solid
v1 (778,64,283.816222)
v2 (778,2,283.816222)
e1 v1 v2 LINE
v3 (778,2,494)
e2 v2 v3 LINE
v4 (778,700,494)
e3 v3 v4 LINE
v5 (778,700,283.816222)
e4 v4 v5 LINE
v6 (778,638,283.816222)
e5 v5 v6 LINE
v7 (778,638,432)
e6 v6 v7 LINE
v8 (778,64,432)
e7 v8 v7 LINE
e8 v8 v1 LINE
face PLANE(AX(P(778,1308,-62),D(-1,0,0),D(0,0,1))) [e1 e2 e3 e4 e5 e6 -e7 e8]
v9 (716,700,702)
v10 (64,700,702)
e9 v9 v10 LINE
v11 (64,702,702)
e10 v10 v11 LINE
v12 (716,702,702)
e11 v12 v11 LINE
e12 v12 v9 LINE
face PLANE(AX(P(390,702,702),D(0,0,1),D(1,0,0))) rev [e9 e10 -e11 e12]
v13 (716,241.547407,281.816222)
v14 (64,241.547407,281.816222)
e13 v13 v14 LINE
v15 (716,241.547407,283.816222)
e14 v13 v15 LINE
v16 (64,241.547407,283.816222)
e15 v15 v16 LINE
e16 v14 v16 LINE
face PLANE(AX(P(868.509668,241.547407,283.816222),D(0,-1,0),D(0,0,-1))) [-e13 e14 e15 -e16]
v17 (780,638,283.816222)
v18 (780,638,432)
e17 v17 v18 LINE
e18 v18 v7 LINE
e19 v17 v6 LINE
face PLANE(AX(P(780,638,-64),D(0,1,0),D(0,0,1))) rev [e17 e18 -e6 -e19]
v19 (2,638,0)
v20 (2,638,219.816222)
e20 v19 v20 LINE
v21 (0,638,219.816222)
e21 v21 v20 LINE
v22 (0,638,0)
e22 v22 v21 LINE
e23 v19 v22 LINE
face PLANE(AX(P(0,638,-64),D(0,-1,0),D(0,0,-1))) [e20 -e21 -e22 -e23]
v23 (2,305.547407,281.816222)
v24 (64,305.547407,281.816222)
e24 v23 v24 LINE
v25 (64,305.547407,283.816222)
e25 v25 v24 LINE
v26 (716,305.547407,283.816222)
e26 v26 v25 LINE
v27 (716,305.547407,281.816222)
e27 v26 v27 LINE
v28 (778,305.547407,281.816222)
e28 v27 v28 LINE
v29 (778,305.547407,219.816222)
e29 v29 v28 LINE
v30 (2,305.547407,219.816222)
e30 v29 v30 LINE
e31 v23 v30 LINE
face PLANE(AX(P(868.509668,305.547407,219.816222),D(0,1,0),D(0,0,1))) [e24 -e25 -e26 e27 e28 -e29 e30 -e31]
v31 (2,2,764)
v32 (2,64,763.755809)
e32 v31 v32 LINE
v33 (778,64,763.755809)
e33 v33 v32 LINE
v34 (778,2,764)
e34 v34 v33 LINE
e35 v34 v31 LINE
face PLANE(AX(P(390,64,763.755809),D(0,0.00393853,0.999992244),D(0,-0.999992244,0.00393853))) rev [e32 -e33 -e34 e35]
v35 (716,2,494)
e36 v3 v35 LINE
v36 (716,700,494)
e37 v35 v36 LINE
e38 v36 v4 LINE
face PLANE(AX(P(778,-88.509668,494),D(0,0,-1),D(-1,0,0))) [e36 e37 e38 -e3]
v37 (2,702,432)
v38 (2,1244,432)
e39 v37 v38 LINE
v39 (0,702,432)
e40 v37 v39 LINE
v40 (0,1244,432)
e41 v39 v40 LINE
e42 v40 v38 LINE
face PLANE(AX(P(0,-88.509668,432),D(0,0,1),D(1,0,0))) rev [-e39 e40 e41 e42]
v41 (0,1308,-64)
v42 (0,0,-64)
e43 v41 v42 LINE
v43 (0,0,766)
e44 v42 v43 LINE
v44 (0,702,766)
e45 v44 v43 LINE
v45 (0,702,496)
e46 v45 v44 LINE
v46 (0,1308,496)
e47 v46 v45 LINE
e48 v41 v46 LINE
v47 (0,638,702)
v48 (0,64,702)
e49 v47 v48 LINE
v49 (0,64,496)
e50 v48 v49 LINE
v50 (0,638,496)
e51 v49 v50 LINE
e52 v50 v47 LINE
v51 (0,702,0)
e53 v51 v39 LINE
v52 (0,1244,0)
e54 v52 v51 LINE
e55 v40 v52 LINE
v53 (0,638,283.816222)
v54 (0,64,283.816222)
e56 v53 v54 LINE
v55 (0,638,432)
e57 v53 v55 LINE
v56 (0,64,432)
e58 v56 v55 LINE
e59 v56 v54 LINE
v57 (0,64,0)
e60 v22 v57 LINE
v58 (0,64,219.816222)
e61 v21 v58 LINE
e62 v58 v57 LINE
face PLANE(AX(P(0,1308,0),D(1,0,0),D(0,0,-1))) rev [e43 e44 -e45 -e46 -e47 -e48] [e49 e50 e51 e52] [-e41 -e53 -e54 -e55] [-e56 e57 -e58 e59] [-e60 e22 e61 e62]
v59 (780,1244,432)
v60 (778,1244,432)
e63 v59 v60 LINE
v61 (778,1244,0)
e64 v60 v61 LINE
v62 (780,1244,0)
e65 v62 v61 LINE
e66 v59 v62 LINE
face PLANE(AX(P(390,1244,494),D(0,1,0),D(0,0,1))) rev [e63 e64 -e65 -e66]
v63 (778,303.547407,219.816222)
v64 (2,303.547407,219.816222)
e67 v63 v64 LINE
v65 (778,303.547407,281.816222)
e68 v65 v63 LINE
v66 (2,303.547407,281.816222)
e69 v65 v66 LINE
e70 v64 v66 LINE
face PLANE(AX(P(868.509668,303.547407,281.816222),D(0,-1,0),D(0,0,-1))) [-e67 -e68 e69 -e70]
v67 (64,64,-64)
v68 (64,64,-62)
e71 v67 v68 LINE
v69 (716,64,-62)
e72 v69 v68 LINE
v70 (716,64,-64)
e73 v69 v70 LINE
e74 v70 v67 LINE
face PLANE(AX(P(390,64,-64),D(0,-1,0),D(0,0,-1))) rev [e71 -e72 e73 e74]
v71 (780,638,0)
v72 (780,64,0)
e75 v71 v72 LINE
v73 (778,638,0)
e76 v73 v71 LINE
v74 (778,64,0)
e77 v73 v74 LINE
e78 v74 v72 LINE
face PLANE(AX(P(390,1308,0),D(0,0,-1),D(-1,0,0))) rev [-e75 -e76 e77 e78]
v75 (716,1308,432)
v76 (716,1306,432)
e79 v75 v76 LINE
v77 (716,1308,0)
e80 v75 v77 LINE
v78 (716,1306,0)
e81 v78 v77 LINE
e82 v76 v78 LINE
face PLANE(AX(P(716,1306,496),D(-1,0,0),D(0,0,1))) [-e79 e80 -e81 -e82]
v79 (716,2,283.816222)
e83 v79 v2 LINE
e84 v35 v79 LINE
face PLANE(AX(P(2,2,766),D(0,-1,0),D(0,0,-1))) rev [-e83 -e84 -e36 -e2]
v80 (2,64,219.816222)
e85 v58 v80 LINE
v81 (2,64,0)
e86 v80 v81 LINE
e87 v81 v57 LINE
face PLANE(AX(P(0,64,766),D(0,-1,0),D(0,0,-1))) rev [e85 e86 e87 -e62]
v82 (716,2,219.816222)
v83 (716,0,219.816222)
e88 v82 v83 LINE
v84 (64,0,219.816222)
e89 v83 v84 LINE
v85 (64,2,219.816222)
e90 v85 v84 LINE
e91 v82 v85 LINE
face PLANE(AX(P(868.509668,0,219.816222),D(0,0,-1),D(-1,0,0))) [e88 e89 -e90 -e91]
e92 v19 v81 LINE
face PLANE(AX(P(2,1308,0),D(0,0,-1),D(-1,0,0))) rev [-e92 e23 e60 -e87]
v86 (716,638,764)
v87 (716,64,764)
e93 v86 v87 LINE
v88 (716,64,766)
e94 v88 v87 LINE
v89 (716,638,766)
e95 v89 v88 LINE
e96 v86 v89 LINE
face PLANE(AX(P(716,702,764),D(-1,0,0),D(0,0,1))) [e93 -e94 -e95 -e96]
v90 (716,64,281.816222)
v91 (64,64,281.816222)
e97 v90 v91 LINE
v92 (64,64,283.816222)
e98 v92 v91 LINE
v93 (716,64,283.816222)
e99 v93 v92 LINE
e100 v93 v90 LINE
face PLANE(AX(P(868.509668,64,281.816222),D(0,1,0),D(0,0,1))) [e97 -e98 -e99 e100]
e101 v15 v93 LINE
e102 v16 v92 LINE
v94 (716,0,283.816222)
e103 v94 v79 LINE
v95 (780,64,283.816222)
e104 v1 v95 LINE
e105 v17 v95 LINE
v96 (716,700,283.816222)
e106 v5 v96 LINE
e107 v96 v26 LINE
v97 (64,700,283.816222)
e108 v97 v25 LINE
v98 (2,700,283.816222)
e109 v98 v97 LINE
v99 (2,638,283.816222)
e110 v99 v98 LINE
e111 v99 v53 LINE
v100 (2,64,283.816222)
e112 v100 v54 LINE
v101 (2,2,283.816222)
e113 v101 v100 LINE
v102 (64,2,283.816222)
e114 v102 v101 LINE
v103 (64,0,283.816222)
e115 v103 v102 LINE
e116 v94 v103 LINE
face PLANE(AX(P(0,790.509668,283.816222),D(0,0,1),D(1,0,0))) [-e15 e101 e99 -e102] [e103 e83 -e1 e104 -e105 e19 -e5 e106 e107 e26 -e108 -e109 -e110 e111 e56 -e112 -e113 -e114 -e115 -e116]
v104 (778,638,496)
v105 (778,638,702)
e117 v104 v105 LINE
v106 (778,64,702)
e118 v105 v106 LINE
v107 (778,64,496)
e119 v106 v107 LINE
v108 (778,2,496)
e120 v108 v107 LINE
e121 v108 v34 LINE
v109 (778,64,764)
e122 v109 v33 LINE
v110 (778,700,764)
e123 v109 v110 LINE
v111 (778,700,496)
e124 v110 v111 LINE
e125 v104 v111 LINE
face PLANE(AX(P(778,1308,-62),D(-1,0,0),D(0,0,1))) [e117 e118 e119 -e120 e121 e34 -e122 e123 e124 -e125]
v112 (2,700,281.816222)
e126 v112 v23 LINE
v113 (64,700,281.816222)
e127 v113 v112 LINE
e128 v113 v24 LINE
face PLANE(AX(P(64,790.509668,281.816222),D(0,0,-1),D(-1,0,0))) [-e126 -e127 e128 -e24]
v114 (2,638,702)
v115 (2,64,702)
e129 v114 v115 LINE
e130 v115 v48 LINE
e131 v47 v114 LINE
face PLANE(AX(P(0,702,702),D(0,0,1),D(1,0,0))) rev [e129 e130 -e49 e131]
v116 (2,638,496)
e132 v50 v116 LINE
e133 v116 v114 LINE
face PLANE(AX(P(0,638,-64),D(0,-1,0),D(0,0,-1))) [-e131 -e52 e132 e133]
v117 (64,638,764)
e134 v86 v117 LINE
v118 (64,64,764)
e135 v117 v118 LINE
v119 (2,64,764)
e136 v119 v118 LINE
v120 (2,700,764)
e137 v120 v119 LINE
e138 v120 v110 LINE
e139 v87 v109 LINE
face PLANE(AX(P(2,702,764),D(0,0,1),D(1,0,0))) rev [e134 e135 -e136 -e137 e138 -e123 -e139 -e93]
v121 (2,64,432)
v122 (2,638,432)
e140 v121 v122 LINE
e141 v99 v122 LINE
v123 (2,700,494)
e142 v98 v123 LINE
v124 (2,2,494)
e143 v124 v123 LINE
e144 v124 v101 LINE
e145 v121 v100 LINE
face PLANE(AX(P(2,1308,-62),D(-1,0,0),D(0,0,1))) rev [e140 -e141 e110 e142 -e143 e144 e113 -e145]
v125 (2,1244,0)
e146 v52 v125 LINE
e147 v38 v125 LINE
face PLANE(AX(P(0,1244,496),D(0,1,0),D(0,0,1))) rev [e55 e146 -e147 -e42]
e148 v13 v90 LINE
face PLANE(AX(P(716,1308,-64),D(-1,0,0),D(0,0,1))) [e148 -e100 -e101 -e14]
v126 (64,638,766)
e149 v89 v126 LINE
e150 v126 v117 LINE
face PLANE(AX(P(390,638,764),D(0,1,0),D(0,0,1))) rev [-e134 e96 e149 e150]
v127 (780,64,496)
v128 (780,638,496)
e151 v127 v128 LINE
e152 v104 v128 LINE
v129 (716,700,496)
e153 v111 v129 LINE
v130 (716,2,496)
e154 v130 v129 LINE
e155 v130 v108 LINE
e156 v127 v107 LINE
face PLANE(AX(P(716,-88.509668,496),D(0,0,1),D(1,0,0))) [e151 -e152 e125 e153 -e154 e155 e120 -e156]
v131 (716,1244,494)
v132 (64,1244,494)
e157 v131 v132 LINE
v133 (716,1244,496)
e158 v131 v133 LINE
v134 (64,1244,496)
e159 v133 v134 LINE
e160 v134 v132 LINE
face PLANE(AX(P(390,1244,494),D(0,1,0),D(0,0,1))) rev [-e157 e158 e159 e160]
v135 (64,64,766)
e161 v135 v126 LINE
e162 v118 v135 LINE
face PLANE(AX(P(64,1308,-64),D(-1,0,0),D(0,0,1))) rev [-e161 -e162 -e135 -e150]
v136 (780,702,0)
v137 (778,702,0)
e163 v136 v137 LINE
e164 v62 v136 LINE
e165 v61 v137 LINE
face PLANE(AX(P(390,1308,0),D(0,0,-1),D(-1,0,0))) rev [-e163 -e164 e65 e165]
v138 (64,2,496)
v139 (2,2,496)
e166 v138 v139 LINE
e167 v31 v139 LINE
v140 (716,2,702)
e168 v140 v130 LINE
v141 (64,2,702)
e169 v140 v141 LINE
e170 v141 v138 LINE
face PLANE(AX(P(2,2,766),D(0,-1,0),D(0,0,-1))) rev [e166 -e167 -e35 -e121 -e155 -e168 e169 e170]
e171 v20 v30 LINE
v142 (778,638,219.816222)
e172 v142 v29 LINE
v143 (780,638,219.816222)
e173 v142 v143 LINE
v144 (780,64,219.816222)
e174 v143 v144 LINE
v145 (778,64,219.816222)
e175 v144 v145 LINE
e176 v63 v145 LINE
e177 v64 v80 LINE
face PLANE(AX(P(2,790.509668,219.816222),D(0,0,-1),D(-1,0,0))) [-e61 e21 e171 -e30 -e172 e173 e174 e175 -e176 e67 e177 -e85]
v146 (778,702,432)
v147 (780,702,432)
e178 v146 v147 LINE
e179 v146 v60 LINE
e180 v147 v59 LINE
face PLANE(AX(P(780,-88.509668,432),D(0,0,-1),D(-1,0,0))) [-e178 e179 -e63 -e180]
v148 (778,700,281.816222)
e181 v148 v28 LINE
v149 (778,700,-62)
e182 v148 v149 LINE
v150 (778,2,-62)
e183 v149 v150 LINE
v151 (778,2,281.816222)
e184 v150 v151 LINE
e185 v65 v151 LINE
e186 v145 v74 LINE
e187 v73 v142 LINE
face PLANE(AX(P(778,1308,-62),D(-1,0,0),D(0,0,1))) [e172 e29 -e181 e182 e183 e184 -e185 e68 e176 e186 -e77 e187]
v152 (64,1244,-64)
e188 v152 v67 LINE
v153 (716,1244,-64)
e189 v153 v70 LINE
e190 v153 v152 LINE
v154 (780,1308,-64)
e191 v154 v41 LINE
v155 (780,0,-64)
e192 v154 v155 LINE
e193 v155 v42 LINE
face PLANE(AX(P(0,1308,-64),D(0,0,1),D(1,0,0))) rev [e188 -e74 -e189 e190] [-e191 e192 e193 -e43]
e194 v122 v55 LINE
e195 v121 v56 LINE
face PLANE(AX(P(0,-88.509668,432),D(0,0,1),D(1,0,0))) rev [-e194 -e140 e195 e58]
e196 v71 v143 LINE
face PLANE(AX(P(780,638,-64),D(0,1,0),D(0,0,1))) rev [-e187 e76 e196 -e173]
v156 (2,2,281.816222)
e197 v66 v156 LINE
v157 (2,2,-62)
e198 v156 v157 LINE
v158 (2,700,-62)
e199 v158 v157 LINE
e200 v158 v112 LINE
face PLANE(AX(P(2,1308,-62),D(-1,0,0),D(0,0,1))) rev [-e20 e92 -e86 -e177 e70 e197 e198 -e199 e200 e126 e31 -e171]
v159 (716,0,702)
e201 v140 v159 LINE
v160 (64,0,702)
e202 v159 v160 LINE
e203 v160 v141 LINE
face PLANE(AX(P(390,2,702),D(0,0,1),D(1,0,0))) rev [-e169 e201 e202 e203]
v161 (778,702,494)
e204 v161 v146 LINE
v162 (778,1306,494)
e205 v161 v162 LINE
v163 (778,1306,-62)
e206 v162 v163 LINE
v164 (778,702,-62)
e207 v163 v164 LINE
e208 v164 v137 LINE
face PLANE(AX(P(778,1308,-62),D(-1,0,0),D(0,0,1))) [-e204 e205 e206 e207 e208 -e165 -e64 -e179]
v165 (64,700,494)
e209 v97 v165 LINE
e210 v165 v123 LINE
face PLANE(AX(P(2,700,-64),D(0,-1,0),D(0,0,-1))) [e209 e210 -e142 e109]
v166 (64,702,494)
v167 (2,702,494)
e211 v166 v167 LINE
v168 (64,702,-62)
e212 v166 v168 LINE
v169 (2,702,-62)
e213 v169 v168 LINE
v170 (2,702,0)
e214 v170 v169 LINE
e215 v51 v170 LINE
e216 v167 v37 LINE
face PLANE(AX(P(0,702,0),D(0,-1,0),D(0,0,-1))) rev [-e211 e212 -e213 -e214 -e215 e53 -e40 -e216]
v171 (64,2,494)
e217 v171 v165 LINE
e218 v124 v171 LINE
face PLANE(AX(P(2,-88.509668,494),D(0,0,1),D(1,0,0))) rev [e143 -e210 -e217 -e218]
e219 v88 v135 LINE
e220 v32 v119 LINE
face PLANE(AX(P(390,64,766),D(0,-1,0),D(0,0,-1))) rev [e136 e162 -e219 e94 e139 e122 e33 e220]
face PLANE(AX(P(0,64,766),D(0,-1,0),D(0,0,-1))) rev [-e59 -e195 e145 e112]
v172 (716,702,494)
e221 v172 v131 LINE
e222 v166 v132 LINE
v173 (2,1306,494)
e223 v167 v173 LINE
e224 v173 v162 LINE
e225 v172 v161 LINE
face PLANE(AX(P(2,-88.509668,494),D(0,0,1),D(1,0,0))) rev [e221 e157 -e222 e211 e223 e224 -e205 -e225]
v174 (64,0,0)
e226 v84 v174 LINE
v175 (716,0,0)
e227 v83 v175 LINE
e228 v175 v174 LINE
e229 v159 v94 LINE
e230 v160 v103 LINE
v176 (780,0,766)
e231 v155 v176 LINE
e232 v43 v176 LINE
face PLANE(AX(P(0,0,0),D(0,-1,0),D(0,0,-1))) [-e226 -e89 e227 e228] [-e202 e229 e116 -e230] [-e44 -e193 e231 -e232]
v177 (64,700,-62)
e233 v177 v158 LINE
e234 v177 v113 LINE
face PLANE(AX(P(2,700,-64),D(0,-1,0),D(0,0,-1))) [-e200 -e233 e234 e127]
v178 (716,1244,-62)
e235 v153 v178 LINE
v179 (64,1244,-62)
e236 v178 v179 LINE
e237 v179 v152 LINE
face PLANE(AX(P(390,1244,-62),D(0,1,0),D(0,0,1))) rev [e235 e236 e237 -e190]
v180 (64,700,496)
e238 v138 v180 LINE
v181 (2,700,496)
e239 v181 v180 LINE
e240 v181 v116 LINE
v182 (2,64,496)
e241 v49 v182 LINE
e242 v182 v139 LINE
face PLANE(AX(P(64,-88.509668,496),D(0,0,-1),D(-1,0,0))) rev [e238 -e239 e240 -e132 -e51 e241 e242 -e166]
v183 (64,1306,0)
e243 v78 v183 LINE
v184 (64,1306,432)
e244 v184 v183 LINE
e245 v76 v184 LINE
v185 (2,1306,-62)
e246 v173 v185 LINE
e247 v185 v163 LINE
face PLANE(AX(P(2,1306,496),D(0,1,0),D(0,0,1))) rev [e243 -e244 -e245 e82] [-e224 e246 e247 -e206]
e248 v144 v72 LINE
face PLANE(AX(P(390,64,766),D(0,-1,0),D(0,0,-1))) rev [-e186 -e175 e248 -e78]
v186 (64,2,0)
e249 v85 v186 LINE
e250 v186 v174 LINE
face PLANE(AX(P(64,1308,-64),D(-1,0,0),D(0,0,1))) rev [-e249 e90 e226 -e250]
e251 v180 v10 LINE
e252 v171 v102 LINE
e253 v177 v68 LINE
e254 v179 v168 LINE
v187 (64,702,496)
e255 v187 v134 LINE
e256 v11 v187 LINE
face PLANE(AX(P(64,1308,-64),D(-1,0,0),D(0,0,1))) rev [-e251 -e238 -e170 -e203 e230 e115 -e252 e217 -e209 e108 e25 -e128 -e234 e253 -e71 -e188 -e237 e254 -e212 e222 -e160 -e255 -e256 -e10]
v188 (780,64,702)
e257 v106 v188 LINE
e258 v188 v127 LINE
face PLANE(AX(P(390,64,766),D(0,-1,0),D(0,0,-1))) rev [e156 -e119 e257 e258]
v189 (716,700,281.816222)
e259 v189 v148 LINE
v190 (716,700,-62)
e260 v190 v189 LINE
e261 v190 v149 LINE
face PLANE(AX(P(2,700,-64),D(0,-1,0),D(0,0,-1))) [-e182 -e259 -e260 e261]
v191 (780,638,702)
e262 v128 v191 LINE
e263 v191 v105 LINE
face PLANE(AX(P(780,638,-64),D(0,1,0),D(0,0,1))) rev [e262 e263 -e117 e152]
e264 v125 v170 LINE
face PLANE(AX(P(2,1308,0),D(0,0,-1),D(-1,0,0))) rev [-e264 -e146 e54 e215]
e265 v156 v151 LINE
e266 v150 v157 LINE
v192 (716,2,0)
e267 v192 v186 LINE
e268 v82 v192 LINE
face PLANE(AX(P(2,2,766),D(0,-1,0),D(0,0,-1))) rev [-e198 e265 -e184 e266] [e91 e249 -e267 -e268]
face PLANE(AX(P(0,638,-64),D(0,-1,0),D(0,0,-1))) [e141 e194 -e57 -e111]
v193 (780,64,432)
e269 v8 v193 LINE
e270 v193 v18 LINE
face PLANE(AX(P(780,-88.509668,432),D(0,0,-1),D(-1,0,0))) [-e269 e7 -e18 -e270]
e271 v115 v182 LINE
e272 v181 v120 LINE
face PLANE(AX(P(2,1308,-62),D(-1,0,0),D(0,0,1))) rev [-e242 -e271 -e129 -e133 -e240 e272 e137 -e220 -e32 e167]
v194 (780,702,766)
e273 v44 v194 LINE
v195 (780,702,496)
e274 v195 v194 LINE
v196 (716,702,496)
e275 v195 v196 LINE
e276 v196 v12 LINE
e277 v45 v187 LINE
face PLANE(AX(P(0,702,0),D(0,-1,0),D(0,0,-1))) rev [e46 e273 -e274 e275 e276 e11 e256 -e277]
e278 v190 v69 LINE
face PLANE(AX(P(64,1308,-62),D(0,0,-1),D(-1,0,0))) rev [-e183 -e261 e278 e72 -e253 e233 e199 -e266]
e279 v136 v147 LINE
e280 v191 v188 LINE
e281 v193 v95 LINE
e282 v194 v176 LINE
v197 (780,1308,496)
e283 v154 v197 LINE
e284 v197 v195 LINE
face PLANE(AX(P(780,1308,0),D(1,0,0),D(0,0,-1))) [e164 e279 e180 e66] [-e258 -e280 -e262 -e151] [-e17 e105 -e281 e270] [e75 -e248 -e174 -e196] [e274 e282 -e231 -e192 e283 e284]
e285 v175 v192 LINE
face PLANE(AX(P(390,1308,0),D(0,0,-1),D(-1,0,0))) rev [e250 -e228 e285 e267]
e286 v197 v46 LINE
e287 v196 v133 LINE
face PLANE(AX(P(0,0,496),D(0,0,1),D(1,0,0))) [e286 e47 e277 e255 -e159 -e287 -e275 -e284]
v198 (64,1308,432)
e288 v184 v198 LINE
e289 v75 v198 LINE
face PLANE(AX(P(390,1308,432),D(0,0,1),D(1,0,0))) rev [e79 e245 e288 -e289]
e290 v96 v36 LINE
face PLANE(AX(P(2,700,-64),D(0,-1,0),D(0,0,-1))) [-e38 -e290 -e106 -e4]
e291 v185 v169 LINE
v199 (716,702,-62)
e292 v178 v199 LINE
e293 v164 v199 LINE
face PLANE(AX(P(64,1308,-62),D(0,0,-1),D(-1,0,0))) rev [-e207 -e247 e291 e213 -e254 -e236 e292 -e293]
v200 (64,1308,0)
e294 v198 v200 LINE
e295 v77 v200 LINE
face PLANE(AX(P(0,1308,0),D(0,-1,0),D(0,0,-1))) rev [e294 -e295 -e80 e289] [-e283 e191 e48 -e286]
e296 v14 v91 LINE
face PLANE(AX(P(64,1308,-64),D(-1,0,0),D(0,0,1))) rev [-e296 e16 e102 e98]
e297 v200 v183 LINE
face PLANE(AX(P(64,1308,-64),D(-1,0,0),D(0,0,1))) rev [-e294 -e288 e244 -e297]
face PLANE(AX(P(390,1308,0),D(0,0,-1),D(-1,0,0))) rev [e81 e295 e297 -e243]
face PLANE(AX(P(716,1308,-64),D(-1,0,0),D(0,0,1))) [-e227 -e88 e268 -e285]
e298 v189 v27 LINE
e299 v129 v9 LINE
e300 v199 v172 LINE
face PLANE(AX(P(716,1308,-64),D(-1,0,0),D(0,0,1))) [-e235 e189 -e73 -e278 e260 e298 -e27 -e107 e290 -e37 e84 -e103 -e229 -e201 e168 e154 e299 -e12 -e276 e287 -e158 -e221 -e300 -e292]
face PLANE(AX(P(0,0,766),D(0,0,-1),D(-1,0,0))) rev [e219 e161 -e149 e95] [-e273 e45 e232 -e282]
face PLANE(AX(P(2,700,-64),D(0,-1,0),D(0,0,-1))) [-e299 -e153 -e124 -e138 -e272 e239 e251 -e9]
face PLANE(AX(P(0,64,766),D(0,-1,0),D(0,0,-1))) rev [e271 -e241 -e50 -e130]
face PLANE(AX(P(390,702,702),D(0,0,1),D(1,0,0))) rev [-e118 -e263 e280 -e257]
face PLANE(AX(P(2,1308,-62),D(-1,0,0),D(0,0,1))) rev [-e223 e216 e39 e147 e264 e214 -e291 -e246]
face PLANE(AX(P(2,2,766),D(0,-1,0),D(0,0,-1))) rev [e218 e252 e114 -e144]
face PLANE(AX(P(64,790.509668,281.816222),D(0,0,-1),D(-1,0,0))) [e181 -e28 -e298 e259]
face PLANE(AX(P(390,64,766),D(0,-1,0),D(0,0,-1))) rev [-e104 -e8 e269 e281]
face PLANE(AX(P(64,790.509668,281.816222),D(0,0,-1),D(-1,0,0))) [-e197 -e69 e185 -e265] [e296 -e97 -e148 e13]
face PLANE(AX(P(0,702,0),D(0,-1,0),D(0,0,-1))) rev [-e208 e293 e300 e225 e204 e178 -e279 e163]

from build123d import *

# Parameters (mm, degrees)
BOSS_EXTRUDE1_DEPTH   = 1308
BOSS_EXTRUDE2_DEPTH   = 828
BOSS_EXTRUDE3_DEPTH   = 700
BOSS_EXTRUDE4_DEPTH   = 828
BOSS_EXTRUDE5_DEPTH   = 558
BOSS_EXTRUDE6_REACH   = 1517.417
BOSS_EXTRUDE8_DEPTH   = 388
MIRROR4_COPY_1_DEPTH  = 1308
MIRROR4_COPY_2_DEPTH  = 828
MIRROR4_COPY_3_DEPTH  = 700
MIRROR4_COPY_4_DEPTH  = 828
MIRROR4_COPY_5_DEPTH  = 558
MIRROR4_COPY_6_REACH  = 1517.417
MIRROR4_COPY_7_DEPTH  = 388
MIRROR4_COPY_8_DEPTH  = 1308
MIRROR4_COPY_9_DEPTH  = 828
MIRROR4_COPY_10_DEPTH = 700
MIRROR4_COPY_11_DEPTH = 828
MIRROR4_COPY_12_DEPTH = 558
MIRROR4_COPY_13_REACH = 1517.417
MIRROR4_COPY_14_DEPTH = 388
BOSS_EXTRUDE9_REACH   = 1706.705
BOSS_EXTRUDE10_DEPTH  = 778
BOSS_EXTRUDE11_START  = -778
BOSS_EXTRUDE11_DEPTH  = 776


with BuildPart() as part:
    # Sketch1 → Boss-Extrude1 (new body)
    with BuildSketch(Plane(origin=(0, 0, 0), x_dir=(1, 0, 0), z_dir=(0, 1, 0))):
        Polygon((0, 0), (0, 64), (64, 64), (64, 62), (2, 62), (2, 0), align=None)
    boss_extrude1 = extrude(amount=BOSS_EXTRUDE1_DEPTH)

    # Sketch2 → Boss-Extrude2 (add)
    with BuildSketch(Plane.XY.offset(-62)):
        Polygon((64, 0), (0, 0), (0, 64), (2, 64), (2, 2), (64, 2), align=None)
    boss_extrude2 = extrude(amount=BOSS_EXTRUDE2_DEPTH)

    # Sketch3 → Boss-Extrude3 (add)
    with BuildSketch(Plane(origin=(0, 2, 0), x_dir=(1, 0, 0), z_dir=(0, 1, 0))):
        Polygon((64, -766), (0, -766), (0, -702), (2, -702), (2, -764), (64, -764), align=None)
    boss_extrude3 = extrude(amount=BOSS_EXTRUDE3_DEPTH)

    # Sketch4 → Boss-Extrude4 (add)
    with BuildSketch(Plane(origin=(0, 0, 764), x_dir=(-1, 0, 0), z_dir=(0, 0, -1))):
        Polygon((-64, 702), (0, 702), (0, 638), (-2, 638), (-2, 700), (-64, 700), align=None)
    boss_extrude4 = extrude(amount=BOSS_EXTRUDE4_DEPTH)

    # Sketch5 → Boss-Extrude5 (add)
    with BuildSketch(Plane.XY.offset(-62)):
        Polygon((64, 1308), (0, 1308), (0, 1244), (2, 1244), (2, 1306), (64, 1306), align=None)
    boss_extrude5 = extrude(amount=BOSS_EXTRUDE5_DEPTH)

    # Boss-Extrude6: up to this face of the body (flat: up to its plane)
    boss_extrude6_end = Plane(part.part.faces().sort_by_distance((33, 2, 351))[0])
    # Sketch6 → Boss-Extrude6 (add, up to the picked face)
    with BuildSketch(Plane.XZ.offset(-1306), mode=Mode.PRIVATE) as boss_extrude6_sk1:
        Polygon((64, 496), (0, 496), (0, 432), (2, 432), (2, 494), (64, 494), align=None)
    boss_extrude6_tool1 = split(extrude(boss_extrude6_sk1.sketch, amount=BOSS_EXTRUDE6_REACH, mode=Mode.PRIVATE), bisect_by=boss_extrude6_end, keep=Keep.BOTH, mode=Mode.PRIVATE)
    boss_extrude6 = boss_extrude6_tool1.solids().sort_by(Axis((32, 1306, 495.094903), (0, -1, 0)))[0]
    add(boss_extrude6)

    # Sketch7 → Boss-Extrude8 (add)
    with BuildSketch(Plane(origin=(2, 0, 0), x_dir=(0, 0, -1), z_dir=(1, 0, 0))):
        Polygon((-496, 1308), (-432, 1308), (-432, 1306), (-494, 1306), (-494, 1244), (-496, 1244), align=None)
        Polygon((64, 1308), (0, 1308), (0, 1306), (62, 1306), (62, 1244), (64, 1244), align=None)
        Polygon((64, 0), (64, 64), (62, 64), (62, 2), (0, 2), (0, 0), align=None)
        Polygon((-766, 0), (-766, 64), (-763.755809275, 64), (-764, 2), (-702, 2), (-702, 0), align=None)
        Polygon((-766, 702), (-702, 702), (-702, 700), (-764, 700), (-764, 638), (-766, 638), align=None)
    boss_extrude8 = extrude(amount=BOSS_EXTRUDE8_DEPTH)

    # Mirror4 copy 1 sketch → Mirror4 copy 1 (add)
    with BuildSketch(Plane(origin=(0, 0, 0), x_dir=(1, 0, 0), z_dir=(0, 1, 0))):
        Polygon((0, 0), (0, 64), (64, 64), (64, 62), (2, 62), (2, 0), align=None)
    extrude(amount=MIRROR4_COPY_1_DEPTH)

    # Mirror4 copy 2 sketch → Mirror4 copy 2 (add)
    with BuildSketch(Plane.XY.offset(-62)):
        Polygon((64, 0), (0, 0), (0, 64), (2, 64), (2, 2), (64, 2), align=None)
    extrude(amount=MIRROR4_COPY_2_DEPTH)

    # Mirror4 copy 3 sketch → Mirror4 copy 3 (add)
    with BuildSketch(Plane(origin=(0, 2, 0), x_dir=(1, 0, 0), z_dir=(0, 1, 0))):
        Polygon((64, -766), (0, -766), (0, -702), (2, -702), (2, -764), (64, -764), align=None)
    extrude(amount=MIRROR4_COPY_3_DEPTH)

    # Mirror4 copy 4 sketch → Mirror4 copy 4 (add)
    with BuildSketch(Plane(origin=(0, 0, 764), x_dir=(-1, 0, 0), z_dir=(0, 0, -1))):
        Polygon((-64, 702), (0, 702), (0, 638), (-2, 638), (-2, 700), (-64, 700), align=None)
    extrude(amount=MIRROR4_COPY_4_DEPTH)

    # Mirror4 copy 5 sketch → Mirror4 copy 5 (add)
    with BuildSketch(Plane.XY.offset(-62)):
        Polygon((64, 1308), (0, 1308), (0, 1244), (2, 1244), (2, 1306), (64, 1306), align=None)
    extrude(amount=MIRROR4_COPY_5_DEPTH)

    # Mirror4 copy 6: up to this face of the body (flat: up to its plane)
    mirror4_copy_6_end = Plane(part.part.faces().sort_by_distance((33, 2, 351))[0])
    # Mirror4 copy 6 sketch → Mirror4 copy 6 (add, up to the picked face)
    with BuildSketch(Plane.XZ.offset(-1306), mode=Mode.PRIVATE) as mirror4_copy_6_sk1:
        Polygon((64, 496), (0, 496), (0, 432), (2, 432), (2, 494), (64, 494), align=None)
    mirror4_copy_6_tool1 = split(extrude(mirror4_copy_6_sk1.sketch, amount=MIRROR4_COPY_6_REACH, mode=Mode.PRIVATE), bisect_by=mirror4_copy_6_end, keep=Keep.BOTH, mode=Mode.PRIVATE)
    add(mirror4_copy_6_tool1.solids().sort_by(Axis((32, 1306, 495.094903), (0, -1, 0)))[0])



with BuildPart() as mirror3_1:
    # Mirror3: Boss-Extrude1, Boss-Extrude2, Boss-Extrude3, Boss-Extrude4, Boss-Extrude5, Boss-Extrude6, Boss-Extrude8 across plane
    add(boss_extrude1.mirror(Plane(origin=(390, 0, 0), x_dir=(0, 0, 1), z_dir=(1, 0, 0))))
    add(boss_extrude2.mirror(Plane(origin=(390, 0, 0), x_dir=(0, 0, 1), z_dir=(1, 0, 0))))
    add(boss_extrude3.mirror(Plane(origin=(390, 0, 0), x_dir=(0, 0, 1), z_dir=(1, 0, 0))))
    add(boss_extrude4.mirror(Plane(origin=(390, 0, 0), x_dir=(0, 0, 1), z_dir=(1, 0, 0))))
    add(boss_extrude5.mirror(Plane(origin=(390, 0, 0), x_dir=(0, 0, 1), z_dir=(1, 0, 0))))
    add(boss_extrude6.mirror(Plane(origin=(390, 0, 0), x_dir=(0, 0, 1), z_dir=(1, 0, 0))))
    add(boss_extrude8.mirror(Plane(origin=(390, 0, 0), x_dir=(0, 0, 1), z_dir=(1, 0, 0))))


with BuildPart() as part_1:
    add(part.part)

    add(mirror3_1.part)  # Mirror4 copy 7 merges Mirror3_1
    # Mirror4 copy 7 sketch → Mirror4 copy 7 (add)
    with BuildSketch(Plane(origin=(2, 0, 0), x_dir=(0, 0, -1), z_dir=(1, 0, 0))):
        Polygon((-496, 1308), (-432, 1308), (-432, 1306), (-494, 1306), (-494, 1244), (-496, 1244), align=None)
        Polygon((64, 1308), (0, 1308), (0, 1306), (62, 1306), (62, 1244), (64, 1244), align=None)
        Polygon((64, 0), (64, 64), (62, 64), (62, 2), (0, 2), (0, 0), align=None)
        Polygon((-766, 0), (-766, 64), (-763.755809275, 64), (-764, 2), (-702, 2), (-702, 0), align=None)
        Polygon((-766, 702), (-702, 702), (-702, 700), (-764, 700), (-764, 638), (-766, 638), align=None)
    extrude(amount=MIRROR4_COPY_7_DEPTH)

    # Mirror4 copy 8 sketch → Mirror4 copy 8 (add)
    with BuildSketch(Plane(origin=(780, 0, 0), x_dir=(-1, 0, 0), z_dir=(0, 1, 0))):
        Polygon((0, 0), (0, -64), (64, -64), (64, -62), (2, -62), (2, 0), align=None)
    extrude(amount=MIRROR4_COPY_8_DEPTH)

    # Mirror4 copy 9 sketch → Mirror4 copy 9 (add)
    with BuildSketch(Plane(origin=(780, 0, -62), x_dir=(-1, 0, 0), z_dir=(0, 0, 1))):
        Polygon((64, 0), (0, 0), (0, -64), (2, -64), (2, -2), (64, -2), align=None)
    extrude(amount=MIRROR4_COPY_9_DEPTH)

    # Mirror4 copy 10 sketch → Mirror4 copy 10 (add)
    with BuildSketch(Plane(origin=(780, 2, 0), x_dir=(-1, 0, 0), z_dir=(0, 1, 0))):
        Polygon((64, 766), (0, 766), (0, 702), (2, 702), (2, 764), (64, 764), align=None)
    extrude(amount=MIRROR4_COPY_10_DEPTH)

    # Mirror4 copy 11 sketch → Mirror4 copy 11 (add)
    with BuildSketch(Plane(origin=(780, 0, 764), x_dir=(1, 0, 0), z_dir=(0, 0, -1))):
        Polygon((-64, -702), (0, -702), (0, -638), (-2, -638), (-2, -700), (-64, -700), align=None)
    extrude(amount=MIRROR4_COPY_11_DEPTH)

    # Mirror4 copy 12 sketch → Mirror4 copy 12 (add)
    with BuildSketch(Plane(origin=(780, 0, -62), x_dir=(-1, 0, 0), z_dir=(0, 0, 1))):
        Polygon((64, -1308), (0, -1308), (0, -1244), (2, -1244), (2, -1306), (64, -1306), align=None)
    extrude(amount=MIRROR4_COPY_12_DEPTH)

    # Mirror4 copy 13: up to this face of the body (flat: up to its plane)
    mirror4_copy_13_end = Plane(part_1.part.faces().sort_by_distance((747, 2, 351))[0])
    # Mirror4 copy 13 sketch → Mirror4 copy 13 (add, up to the picked face)
    with BuildSketch(Plane(origin=(780, 1306, 0), x_dir=(-1, 0, 0), z_dir=(0, -1, 0)), mode=Mode.PRIVATE) as mirror4_copy_13_sk1:
        Polygon((64, -496), (0, -496), (0, -432), (2, -432), (2, -494), (64, -494), align=None)
    mirror4_copy_13_tool1 = split(extrude(mirror4_copy_13_sk1.sketch, amount=MIRROR4_COPY_13_REACH, mode=Mode.PRIVATE), bisect_by=mirror4_copy_13_end, keep=Keep.BOTH, mode=Mode.PRIVATE)
    add(mirror4_copy_13_tool1.solids().sort_by(Axis((748, 1306, 495.094903), (0, -1, 0)))[0])

    # Mirror4 copy 14 sketch → Mirror4 copy 14 (add)
    with BuildSketch(Plane(origin=(778, 0, 0), x_dir=(0, 0, -1), z_dir=(-1, 0, 0))):
        Polygon((-496, -1308), (-432, -1308), (-432, -1306), (-494, -1306), (-494, -1244), (-496, -1244), align=None)
        Polygon((64, -1308), (0, -1308), (0, -1306), (62, -1306), (62, -1244), (64, -1244), align=None)
        Polygon((64, 0), (64, -64), (62, -64), (62, -2), (0, -2), (0, 0), align=None)
        Polygon((-766, 0), (-766, -64), (-763.755809275, -64), (-764, -2), (-702, -2), (-702, 0), align=None)
        Polygon((-766, -702), (-702, -702), (-702, -700), (-764, -700), (-764, -638), (-766, -638), align=None)
    extrude(amount=MIRROR4_COPY_14_DEPTH)

    # Boss-Extrude9: up to this face of the body (flat: up to its plane)
    boss_extrude9_end = Plane(part_1.part.faces().sort_by_distance((33, 700, 216))[0])
    # Sketch8 → Boss-Extrude9 (add, up to the picked face)
    with BuildSketch(Plane.XZ, mode=Mode.PRIVATE) as boss_extrude9_sk1:
        Polygon((0, 283.816221782), (64, 283.816221782), (64, 281.816221782), (2, 281.816221782), (2, 219.816221782), (0, 219.816221782), align=None)
    boss_extrude9_tool1 = split(extrude(boss_extrude9_sk1.sketch, amount=-BOSS_EXTRUDE9_REACH, mode=Mode.PRIVATE), bisect_by=boss_extrude9_end, keep=Keep.BOTH, mode=Mode.PRIVATE)
    boss_extrude9 = boss_extrude9_tool1.solids().sort_by(Axis((32, 0, 282.911125), (0, 1, 0)))[0]
    add(boss_extrude9)

    # Mirror5: Boss-Extrude9 across plane
    add(boss_extrude9.mirror(Plane(origin=(390, 0, 0), x_dir=(0, 0, 1), z_dir=(1, 0, 0))))

    # Sketch9 → Boss-Extrude10 (add)
    with BuildSketch(Plane.ZY):
        Polygon((283.816221782, 64), (283.816221782, 0), (219.816221782, 0), (219.816221782, 2), (281.816221782, 2), (281.816221782, 64), align=None)
    extrude(amount=-BOSS_EXTRUDE10_DEPTH)

    # Sketch10 → Boss-Extrude11 (add)
    with BuildSketch(Plane.ZY.offset(BOSS_EXTRUDE11_START)):
        Polygon((219.816221782, 305.547407483), (283.816221782, 305.547407483), (283.816221782, 241.547407483), (281.816221782, 241.547407483), (281.816221782, 303.547407483), (219.816221782, 303.547407483), align=None)
    extrude(amount=BOSS_EXTRUDE11_DEPTH)


solid = part_1.part
